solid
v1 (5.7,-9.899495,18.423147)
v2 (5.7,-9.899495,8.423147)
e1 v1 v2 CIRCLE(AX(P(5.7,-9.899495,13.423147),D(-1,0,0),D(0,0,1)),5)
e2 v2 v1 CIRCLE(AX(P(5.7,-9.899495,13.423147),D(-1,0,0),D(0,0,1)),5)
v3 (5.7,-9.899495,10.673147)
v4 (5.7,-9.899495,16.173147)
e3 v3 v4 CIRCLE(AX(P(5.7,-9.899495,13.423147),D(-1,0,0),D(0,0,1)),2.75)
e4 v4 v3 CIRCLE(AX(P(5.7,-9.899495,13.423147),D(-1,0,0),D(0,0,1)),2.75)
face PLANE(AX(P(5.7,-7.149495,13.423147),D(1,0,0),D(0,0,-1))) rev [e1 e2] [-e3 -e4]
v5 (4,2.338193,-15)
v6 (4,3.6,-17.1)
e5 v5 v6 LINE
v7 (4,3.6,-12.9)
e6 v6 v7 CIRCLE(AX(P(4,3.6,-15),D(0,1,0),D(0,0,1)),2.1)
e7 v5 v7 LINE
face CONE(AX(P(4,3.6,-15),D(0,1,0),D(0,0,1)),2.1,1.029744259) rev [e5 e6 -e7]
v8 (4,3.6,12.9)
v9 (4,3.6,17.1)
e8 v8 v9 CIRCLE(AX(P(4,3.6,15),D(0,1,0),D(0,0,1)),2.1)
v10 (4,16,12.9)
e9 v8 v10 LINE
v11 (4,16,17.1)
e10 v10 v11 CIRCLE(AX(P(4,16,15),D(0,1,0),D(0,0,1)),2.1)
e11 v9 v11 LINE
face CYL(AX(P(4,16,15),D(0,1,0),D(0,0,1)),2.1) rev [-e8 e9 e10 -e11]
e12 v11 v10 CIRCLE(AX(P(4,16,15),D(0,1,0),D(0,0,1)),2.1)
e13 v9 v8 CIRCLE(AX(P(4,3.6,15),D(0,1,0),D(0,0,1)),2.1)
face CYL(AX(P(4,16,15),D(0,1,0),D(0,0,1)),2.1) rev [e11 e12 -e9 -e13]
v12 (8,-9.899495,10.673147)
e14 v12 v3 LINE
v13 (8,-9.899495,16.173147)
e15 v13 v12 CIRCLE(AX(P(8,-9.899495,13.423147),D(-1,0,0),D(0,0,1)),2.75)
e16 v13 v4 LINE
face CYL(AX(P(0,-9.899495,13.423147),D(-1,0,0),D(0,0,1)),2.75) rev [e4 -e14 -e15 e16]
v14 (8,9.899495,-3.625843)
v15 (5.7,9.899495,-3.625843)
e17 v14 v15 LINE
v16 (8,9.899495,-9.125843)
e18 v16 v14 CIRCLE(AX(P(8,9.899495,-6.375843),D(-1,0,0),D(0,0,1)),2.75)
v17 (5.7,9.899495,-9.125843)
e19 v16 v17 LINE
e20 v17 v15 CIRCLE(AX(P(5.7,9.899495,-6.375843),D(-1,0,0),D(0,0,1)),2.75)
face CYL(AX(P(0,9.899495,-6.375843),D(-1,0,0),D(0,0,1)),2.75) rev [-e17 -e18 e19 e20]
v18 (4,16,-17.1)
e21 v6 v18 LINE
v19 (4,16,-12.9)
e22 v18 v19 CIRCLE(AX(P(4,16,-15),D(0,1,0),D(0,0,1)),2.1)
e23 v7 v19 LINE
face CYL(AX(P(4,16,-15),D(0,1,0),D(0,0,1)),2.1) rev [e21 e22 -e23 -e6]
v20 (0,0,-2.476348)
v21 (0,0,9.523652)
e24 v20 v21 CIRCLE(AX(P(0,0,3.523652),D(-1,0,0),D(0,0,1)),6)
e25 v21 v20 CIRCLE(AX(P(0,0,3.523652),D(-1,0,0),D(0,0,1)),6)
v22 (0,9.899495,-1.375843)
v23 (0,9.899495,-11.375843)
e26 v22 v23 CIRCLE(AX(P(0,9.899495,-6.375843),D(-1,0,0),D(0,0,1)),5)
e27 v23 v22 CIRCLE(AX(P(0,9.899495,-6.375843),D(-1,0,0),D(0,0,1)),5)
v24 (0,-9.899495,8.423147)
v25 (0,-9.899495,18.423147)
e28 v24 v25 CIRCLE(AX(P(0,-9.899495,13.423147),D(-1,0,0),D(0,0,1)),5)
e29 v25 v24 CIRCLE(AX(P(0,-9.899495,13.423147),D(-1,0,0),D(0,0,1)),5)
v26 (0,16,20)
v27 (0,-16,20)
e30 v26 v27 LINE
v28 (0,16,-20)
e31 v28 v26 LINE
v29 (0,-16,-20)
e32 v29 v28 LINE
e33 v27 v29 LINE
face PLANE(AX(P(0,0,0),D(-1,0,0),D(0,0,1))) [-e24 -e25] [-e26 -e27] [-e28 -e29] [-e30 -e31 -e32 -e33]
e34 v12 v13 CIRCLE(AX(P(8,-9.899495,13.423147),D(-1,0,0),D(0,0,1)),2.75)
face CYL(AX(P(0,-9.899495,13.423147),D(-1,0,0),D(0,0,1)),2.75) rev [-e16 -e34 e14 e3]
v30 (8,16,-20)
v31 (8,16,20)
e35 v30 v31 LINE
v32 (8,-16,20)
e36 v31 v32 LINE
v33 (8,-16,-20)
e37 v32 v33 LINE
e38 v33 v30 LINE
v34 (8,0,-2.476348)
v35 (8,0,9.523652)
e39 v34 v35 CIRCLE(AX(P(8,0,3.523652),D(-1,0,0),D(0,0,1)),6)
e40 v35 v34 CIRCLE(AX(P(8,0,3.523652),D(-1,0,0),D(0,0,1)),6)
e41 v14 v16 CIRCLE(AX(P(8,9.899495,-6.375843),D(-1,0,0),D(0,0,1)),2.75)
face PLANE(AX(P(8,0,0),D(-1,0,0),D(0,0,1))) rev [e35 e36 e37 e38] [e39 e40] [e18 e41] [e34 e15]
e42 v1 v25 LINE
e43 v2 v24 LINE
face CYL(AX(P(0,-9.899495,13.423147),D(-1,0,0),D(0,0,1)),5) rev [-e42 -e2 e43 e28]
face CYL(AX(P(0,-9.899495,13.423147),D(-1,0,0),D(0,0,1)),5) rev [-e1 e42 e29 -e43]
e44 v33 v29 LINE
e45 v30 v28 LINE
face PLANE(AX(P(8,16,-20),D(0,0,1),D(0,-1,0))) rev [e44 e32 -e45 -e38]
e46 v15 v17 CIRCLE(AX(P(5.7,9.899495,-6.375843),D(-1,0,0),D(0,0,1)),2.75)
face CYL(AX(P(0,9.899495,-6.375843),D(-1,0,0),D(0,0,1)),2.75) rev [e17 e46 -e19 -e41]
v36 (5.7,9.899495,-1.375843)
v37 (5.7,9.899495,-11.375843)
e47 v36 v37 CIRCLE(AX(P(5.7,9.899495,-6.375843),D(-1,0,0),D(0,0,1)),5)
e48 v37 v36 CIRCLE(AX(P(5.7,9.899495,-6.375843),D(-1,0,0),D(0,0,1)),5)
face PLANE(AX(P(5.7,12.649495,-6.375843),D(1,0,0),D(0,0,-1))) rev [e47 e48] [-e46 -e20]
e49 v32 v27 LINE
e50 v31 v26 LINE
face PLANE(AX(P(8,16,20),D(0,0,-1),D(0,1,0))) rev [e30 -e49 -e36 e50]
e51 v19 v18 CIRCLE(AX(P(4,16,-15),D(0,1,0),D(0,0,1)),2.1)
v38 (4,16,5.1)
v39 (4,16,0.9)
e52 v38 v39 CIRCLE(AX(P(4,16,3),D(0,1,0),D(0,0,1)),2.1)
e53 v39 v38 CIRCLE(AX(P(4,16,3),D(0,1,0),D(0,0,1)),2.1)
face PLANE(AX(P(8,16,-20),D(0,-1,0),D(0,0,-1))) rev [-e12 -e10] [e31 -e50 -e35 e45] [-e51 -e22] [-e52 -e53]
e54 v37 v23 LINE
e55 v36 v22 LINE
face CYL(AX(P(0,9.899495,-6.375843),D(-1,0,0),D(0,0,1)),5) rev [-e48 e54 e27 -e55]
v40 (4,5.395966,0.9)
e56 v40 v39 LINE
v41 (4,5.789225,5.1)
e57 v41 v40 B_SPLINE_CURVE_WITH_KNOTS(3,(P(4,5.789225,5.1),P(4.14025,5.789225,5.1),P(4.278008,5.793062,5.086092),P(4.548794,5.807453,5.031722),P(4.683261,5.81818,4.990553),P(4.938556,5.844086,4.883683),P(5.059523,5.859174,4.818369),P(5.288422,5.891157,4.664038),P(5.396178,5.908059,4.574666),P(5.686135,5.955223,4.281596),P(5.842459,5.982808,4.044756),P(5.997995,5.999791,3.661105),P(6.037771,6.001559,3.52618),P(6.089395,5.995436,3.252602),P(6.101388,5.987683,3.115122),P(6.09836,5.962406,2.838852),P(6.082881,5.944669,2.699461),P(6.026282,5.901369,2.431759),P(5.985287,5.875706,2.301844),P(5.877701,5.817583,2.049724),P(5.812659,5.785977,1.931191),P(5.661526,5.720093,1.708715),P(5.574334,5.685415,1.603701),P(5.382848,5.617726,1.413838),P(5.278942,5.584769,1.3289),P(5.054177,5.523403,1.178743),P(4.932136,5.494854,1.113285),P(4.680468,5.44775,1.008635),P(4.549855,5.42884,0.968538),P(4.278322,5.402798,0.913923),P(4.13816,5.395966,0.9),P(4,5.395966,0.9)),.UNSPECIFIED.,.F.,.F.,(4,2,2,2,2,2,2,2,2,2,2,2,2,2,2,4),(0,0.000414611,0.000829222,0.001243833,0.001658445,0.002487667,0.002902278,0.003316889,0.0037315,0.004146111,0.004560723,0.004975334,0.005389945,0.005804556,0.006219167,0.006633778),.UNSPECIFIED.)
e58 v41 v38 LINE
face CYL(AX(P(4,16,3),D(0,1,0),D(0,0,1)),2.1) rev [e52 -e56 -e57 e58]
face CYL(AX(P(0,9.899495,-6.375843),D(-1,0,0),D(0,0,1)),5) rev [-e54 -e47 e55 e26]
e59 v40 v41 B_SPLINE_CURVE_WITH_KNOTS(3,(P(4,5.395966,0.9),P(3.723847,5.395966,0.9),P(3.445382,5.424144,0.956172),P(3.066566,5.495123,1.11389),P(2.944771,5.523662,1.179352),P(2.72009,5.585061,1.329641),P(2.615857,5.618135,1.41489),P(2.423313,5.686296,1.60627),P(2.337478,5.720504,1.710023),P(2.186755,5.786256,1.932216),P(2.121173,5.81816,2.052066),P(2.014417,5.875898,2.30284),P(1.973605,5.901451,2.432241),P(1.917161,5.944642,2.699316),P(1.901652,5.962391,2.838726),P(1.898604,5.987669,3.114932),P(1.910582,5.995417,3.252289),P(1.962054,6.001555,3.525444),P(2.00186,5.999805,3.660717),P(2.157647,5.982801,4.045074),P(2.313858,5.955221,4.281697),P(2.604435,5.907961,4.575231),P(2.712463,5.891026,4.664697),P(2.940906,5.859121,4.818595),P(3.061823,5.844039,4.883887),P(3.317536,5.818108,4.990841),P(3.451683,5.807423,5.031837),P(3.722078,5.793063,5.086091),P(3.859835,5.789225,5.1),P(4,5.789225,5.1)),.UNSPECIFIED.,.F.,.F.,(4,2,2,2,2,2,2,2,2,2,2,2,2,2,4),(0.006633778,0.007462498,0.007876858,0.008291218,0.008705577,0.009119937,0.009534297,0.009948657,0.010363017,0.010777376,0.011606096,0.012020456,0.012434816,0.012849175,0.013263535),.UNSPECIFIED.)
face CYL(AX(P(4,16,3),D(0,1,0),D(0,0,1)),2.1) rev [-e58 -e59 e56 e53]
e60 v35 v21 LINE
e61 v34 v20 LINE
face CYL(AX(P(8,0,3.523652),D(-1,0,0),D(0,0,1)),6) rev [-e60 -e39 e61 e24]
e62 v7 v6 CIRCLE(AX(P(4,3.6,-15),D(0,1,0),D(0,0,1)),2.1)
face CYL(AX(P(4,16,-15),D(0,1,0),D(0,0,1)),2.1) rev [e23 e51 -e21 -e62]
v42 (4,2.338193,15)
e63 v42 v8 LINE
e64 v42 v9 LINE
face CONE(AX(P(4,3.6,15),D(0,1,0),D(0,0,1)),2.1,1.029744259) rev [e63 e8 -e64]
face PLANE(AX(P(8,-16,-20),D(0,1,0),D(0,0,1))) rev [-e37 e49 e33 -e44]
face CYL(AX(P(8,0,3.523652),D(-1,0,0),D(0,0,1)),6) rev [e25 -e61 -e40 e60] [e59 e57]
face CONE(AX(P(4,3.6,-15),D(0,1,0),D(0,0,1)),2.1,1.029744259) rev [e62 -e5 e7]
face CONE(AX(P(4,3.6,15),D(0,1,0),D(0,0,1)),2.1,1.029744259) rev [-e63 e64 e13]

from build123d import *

# Parameters (mm, degrees)
SKETCH_1_W                = 40
SKETCH_1_H                = 32
EXTRUDE_1_DEPTH           = 8
SKETCH_8_R                = 6
CUT_EXTRUDE_2_DEPTH       = 27.83281573
HOLE_WIZARD_3_D           = 5.5
HOLE_WIZARD_3_CBORE_D     = 10
HOLE_WIZARD_3_CBORE_DEPTH = 5.7
HOLE_WIZARD_M5_1_D        = 4.2
HOLE_WIZARD_M5_1_DEPTH    = 12.4
HOLE_WIZARD_M5_1_TIP      = 1.2618073


with BuildPart() as part:
    # 草图1 → 凸台-拉伸1 (new body)
    with BuildSketch(Plane(origin=(0, 0, 0), x_dir=(0, 0, -1), z_dir=(1, 0, 0))):
        Rectangle(SKETCH_1_W, SKETCH_1_H)
    extrude(amount=EXTRUDE_1_DEPTH)

    # 草图8 → 切除-拉伸2 (cut, through all)
    with BuildSketch(Plane.ZY):
        with Locations((3.523652159, 0)):
            Circle(SKETCH_8_R)
    extrude(amount=-CUT_EXTRUDE_2_DEPTH, mode=Mode.SUBTRACT)

    # 打孔尺寸(%根据)内六角圆柱头螺钉的类型3 (through all)
    with Locations(Plane.ZY):
        with Locations((-6.375842777, 9.899494937), (13.423147096, -9.899494937)):
            CounterBoreHole(HOLE_WIZARD_3_D / 2, HOLE_WIZARD_3_CBORE_D / 2, HOLE_WIZARD_3_CBORE_DEPTH)

    # M5 螺纹孔1
    with Locations(Plane(origin=(0, 16, 0), x_dir=(1, 0, 0), z_dir=(0, 1, 0))):
        with Locations((4, -3), (4, -15), (4, 15)):
            Hole(HOLE_WIZARD_M5_1_D / 2, depth=HOLE_WIZARD_M5_1_DEPTH)
            with Locations((0, 0, -(HOLE_WIZARD_M5_1_DEPTH + HOLE_WIZARD_M5_1_TIP / 2))):  # 118° drill point
                Cone(0, HOLE_WIZARD_M5_1_D / 2, HOLE_WIZARD_M5_1_TIP, mode=Mode.SUBTRACT)


solid = part.part
